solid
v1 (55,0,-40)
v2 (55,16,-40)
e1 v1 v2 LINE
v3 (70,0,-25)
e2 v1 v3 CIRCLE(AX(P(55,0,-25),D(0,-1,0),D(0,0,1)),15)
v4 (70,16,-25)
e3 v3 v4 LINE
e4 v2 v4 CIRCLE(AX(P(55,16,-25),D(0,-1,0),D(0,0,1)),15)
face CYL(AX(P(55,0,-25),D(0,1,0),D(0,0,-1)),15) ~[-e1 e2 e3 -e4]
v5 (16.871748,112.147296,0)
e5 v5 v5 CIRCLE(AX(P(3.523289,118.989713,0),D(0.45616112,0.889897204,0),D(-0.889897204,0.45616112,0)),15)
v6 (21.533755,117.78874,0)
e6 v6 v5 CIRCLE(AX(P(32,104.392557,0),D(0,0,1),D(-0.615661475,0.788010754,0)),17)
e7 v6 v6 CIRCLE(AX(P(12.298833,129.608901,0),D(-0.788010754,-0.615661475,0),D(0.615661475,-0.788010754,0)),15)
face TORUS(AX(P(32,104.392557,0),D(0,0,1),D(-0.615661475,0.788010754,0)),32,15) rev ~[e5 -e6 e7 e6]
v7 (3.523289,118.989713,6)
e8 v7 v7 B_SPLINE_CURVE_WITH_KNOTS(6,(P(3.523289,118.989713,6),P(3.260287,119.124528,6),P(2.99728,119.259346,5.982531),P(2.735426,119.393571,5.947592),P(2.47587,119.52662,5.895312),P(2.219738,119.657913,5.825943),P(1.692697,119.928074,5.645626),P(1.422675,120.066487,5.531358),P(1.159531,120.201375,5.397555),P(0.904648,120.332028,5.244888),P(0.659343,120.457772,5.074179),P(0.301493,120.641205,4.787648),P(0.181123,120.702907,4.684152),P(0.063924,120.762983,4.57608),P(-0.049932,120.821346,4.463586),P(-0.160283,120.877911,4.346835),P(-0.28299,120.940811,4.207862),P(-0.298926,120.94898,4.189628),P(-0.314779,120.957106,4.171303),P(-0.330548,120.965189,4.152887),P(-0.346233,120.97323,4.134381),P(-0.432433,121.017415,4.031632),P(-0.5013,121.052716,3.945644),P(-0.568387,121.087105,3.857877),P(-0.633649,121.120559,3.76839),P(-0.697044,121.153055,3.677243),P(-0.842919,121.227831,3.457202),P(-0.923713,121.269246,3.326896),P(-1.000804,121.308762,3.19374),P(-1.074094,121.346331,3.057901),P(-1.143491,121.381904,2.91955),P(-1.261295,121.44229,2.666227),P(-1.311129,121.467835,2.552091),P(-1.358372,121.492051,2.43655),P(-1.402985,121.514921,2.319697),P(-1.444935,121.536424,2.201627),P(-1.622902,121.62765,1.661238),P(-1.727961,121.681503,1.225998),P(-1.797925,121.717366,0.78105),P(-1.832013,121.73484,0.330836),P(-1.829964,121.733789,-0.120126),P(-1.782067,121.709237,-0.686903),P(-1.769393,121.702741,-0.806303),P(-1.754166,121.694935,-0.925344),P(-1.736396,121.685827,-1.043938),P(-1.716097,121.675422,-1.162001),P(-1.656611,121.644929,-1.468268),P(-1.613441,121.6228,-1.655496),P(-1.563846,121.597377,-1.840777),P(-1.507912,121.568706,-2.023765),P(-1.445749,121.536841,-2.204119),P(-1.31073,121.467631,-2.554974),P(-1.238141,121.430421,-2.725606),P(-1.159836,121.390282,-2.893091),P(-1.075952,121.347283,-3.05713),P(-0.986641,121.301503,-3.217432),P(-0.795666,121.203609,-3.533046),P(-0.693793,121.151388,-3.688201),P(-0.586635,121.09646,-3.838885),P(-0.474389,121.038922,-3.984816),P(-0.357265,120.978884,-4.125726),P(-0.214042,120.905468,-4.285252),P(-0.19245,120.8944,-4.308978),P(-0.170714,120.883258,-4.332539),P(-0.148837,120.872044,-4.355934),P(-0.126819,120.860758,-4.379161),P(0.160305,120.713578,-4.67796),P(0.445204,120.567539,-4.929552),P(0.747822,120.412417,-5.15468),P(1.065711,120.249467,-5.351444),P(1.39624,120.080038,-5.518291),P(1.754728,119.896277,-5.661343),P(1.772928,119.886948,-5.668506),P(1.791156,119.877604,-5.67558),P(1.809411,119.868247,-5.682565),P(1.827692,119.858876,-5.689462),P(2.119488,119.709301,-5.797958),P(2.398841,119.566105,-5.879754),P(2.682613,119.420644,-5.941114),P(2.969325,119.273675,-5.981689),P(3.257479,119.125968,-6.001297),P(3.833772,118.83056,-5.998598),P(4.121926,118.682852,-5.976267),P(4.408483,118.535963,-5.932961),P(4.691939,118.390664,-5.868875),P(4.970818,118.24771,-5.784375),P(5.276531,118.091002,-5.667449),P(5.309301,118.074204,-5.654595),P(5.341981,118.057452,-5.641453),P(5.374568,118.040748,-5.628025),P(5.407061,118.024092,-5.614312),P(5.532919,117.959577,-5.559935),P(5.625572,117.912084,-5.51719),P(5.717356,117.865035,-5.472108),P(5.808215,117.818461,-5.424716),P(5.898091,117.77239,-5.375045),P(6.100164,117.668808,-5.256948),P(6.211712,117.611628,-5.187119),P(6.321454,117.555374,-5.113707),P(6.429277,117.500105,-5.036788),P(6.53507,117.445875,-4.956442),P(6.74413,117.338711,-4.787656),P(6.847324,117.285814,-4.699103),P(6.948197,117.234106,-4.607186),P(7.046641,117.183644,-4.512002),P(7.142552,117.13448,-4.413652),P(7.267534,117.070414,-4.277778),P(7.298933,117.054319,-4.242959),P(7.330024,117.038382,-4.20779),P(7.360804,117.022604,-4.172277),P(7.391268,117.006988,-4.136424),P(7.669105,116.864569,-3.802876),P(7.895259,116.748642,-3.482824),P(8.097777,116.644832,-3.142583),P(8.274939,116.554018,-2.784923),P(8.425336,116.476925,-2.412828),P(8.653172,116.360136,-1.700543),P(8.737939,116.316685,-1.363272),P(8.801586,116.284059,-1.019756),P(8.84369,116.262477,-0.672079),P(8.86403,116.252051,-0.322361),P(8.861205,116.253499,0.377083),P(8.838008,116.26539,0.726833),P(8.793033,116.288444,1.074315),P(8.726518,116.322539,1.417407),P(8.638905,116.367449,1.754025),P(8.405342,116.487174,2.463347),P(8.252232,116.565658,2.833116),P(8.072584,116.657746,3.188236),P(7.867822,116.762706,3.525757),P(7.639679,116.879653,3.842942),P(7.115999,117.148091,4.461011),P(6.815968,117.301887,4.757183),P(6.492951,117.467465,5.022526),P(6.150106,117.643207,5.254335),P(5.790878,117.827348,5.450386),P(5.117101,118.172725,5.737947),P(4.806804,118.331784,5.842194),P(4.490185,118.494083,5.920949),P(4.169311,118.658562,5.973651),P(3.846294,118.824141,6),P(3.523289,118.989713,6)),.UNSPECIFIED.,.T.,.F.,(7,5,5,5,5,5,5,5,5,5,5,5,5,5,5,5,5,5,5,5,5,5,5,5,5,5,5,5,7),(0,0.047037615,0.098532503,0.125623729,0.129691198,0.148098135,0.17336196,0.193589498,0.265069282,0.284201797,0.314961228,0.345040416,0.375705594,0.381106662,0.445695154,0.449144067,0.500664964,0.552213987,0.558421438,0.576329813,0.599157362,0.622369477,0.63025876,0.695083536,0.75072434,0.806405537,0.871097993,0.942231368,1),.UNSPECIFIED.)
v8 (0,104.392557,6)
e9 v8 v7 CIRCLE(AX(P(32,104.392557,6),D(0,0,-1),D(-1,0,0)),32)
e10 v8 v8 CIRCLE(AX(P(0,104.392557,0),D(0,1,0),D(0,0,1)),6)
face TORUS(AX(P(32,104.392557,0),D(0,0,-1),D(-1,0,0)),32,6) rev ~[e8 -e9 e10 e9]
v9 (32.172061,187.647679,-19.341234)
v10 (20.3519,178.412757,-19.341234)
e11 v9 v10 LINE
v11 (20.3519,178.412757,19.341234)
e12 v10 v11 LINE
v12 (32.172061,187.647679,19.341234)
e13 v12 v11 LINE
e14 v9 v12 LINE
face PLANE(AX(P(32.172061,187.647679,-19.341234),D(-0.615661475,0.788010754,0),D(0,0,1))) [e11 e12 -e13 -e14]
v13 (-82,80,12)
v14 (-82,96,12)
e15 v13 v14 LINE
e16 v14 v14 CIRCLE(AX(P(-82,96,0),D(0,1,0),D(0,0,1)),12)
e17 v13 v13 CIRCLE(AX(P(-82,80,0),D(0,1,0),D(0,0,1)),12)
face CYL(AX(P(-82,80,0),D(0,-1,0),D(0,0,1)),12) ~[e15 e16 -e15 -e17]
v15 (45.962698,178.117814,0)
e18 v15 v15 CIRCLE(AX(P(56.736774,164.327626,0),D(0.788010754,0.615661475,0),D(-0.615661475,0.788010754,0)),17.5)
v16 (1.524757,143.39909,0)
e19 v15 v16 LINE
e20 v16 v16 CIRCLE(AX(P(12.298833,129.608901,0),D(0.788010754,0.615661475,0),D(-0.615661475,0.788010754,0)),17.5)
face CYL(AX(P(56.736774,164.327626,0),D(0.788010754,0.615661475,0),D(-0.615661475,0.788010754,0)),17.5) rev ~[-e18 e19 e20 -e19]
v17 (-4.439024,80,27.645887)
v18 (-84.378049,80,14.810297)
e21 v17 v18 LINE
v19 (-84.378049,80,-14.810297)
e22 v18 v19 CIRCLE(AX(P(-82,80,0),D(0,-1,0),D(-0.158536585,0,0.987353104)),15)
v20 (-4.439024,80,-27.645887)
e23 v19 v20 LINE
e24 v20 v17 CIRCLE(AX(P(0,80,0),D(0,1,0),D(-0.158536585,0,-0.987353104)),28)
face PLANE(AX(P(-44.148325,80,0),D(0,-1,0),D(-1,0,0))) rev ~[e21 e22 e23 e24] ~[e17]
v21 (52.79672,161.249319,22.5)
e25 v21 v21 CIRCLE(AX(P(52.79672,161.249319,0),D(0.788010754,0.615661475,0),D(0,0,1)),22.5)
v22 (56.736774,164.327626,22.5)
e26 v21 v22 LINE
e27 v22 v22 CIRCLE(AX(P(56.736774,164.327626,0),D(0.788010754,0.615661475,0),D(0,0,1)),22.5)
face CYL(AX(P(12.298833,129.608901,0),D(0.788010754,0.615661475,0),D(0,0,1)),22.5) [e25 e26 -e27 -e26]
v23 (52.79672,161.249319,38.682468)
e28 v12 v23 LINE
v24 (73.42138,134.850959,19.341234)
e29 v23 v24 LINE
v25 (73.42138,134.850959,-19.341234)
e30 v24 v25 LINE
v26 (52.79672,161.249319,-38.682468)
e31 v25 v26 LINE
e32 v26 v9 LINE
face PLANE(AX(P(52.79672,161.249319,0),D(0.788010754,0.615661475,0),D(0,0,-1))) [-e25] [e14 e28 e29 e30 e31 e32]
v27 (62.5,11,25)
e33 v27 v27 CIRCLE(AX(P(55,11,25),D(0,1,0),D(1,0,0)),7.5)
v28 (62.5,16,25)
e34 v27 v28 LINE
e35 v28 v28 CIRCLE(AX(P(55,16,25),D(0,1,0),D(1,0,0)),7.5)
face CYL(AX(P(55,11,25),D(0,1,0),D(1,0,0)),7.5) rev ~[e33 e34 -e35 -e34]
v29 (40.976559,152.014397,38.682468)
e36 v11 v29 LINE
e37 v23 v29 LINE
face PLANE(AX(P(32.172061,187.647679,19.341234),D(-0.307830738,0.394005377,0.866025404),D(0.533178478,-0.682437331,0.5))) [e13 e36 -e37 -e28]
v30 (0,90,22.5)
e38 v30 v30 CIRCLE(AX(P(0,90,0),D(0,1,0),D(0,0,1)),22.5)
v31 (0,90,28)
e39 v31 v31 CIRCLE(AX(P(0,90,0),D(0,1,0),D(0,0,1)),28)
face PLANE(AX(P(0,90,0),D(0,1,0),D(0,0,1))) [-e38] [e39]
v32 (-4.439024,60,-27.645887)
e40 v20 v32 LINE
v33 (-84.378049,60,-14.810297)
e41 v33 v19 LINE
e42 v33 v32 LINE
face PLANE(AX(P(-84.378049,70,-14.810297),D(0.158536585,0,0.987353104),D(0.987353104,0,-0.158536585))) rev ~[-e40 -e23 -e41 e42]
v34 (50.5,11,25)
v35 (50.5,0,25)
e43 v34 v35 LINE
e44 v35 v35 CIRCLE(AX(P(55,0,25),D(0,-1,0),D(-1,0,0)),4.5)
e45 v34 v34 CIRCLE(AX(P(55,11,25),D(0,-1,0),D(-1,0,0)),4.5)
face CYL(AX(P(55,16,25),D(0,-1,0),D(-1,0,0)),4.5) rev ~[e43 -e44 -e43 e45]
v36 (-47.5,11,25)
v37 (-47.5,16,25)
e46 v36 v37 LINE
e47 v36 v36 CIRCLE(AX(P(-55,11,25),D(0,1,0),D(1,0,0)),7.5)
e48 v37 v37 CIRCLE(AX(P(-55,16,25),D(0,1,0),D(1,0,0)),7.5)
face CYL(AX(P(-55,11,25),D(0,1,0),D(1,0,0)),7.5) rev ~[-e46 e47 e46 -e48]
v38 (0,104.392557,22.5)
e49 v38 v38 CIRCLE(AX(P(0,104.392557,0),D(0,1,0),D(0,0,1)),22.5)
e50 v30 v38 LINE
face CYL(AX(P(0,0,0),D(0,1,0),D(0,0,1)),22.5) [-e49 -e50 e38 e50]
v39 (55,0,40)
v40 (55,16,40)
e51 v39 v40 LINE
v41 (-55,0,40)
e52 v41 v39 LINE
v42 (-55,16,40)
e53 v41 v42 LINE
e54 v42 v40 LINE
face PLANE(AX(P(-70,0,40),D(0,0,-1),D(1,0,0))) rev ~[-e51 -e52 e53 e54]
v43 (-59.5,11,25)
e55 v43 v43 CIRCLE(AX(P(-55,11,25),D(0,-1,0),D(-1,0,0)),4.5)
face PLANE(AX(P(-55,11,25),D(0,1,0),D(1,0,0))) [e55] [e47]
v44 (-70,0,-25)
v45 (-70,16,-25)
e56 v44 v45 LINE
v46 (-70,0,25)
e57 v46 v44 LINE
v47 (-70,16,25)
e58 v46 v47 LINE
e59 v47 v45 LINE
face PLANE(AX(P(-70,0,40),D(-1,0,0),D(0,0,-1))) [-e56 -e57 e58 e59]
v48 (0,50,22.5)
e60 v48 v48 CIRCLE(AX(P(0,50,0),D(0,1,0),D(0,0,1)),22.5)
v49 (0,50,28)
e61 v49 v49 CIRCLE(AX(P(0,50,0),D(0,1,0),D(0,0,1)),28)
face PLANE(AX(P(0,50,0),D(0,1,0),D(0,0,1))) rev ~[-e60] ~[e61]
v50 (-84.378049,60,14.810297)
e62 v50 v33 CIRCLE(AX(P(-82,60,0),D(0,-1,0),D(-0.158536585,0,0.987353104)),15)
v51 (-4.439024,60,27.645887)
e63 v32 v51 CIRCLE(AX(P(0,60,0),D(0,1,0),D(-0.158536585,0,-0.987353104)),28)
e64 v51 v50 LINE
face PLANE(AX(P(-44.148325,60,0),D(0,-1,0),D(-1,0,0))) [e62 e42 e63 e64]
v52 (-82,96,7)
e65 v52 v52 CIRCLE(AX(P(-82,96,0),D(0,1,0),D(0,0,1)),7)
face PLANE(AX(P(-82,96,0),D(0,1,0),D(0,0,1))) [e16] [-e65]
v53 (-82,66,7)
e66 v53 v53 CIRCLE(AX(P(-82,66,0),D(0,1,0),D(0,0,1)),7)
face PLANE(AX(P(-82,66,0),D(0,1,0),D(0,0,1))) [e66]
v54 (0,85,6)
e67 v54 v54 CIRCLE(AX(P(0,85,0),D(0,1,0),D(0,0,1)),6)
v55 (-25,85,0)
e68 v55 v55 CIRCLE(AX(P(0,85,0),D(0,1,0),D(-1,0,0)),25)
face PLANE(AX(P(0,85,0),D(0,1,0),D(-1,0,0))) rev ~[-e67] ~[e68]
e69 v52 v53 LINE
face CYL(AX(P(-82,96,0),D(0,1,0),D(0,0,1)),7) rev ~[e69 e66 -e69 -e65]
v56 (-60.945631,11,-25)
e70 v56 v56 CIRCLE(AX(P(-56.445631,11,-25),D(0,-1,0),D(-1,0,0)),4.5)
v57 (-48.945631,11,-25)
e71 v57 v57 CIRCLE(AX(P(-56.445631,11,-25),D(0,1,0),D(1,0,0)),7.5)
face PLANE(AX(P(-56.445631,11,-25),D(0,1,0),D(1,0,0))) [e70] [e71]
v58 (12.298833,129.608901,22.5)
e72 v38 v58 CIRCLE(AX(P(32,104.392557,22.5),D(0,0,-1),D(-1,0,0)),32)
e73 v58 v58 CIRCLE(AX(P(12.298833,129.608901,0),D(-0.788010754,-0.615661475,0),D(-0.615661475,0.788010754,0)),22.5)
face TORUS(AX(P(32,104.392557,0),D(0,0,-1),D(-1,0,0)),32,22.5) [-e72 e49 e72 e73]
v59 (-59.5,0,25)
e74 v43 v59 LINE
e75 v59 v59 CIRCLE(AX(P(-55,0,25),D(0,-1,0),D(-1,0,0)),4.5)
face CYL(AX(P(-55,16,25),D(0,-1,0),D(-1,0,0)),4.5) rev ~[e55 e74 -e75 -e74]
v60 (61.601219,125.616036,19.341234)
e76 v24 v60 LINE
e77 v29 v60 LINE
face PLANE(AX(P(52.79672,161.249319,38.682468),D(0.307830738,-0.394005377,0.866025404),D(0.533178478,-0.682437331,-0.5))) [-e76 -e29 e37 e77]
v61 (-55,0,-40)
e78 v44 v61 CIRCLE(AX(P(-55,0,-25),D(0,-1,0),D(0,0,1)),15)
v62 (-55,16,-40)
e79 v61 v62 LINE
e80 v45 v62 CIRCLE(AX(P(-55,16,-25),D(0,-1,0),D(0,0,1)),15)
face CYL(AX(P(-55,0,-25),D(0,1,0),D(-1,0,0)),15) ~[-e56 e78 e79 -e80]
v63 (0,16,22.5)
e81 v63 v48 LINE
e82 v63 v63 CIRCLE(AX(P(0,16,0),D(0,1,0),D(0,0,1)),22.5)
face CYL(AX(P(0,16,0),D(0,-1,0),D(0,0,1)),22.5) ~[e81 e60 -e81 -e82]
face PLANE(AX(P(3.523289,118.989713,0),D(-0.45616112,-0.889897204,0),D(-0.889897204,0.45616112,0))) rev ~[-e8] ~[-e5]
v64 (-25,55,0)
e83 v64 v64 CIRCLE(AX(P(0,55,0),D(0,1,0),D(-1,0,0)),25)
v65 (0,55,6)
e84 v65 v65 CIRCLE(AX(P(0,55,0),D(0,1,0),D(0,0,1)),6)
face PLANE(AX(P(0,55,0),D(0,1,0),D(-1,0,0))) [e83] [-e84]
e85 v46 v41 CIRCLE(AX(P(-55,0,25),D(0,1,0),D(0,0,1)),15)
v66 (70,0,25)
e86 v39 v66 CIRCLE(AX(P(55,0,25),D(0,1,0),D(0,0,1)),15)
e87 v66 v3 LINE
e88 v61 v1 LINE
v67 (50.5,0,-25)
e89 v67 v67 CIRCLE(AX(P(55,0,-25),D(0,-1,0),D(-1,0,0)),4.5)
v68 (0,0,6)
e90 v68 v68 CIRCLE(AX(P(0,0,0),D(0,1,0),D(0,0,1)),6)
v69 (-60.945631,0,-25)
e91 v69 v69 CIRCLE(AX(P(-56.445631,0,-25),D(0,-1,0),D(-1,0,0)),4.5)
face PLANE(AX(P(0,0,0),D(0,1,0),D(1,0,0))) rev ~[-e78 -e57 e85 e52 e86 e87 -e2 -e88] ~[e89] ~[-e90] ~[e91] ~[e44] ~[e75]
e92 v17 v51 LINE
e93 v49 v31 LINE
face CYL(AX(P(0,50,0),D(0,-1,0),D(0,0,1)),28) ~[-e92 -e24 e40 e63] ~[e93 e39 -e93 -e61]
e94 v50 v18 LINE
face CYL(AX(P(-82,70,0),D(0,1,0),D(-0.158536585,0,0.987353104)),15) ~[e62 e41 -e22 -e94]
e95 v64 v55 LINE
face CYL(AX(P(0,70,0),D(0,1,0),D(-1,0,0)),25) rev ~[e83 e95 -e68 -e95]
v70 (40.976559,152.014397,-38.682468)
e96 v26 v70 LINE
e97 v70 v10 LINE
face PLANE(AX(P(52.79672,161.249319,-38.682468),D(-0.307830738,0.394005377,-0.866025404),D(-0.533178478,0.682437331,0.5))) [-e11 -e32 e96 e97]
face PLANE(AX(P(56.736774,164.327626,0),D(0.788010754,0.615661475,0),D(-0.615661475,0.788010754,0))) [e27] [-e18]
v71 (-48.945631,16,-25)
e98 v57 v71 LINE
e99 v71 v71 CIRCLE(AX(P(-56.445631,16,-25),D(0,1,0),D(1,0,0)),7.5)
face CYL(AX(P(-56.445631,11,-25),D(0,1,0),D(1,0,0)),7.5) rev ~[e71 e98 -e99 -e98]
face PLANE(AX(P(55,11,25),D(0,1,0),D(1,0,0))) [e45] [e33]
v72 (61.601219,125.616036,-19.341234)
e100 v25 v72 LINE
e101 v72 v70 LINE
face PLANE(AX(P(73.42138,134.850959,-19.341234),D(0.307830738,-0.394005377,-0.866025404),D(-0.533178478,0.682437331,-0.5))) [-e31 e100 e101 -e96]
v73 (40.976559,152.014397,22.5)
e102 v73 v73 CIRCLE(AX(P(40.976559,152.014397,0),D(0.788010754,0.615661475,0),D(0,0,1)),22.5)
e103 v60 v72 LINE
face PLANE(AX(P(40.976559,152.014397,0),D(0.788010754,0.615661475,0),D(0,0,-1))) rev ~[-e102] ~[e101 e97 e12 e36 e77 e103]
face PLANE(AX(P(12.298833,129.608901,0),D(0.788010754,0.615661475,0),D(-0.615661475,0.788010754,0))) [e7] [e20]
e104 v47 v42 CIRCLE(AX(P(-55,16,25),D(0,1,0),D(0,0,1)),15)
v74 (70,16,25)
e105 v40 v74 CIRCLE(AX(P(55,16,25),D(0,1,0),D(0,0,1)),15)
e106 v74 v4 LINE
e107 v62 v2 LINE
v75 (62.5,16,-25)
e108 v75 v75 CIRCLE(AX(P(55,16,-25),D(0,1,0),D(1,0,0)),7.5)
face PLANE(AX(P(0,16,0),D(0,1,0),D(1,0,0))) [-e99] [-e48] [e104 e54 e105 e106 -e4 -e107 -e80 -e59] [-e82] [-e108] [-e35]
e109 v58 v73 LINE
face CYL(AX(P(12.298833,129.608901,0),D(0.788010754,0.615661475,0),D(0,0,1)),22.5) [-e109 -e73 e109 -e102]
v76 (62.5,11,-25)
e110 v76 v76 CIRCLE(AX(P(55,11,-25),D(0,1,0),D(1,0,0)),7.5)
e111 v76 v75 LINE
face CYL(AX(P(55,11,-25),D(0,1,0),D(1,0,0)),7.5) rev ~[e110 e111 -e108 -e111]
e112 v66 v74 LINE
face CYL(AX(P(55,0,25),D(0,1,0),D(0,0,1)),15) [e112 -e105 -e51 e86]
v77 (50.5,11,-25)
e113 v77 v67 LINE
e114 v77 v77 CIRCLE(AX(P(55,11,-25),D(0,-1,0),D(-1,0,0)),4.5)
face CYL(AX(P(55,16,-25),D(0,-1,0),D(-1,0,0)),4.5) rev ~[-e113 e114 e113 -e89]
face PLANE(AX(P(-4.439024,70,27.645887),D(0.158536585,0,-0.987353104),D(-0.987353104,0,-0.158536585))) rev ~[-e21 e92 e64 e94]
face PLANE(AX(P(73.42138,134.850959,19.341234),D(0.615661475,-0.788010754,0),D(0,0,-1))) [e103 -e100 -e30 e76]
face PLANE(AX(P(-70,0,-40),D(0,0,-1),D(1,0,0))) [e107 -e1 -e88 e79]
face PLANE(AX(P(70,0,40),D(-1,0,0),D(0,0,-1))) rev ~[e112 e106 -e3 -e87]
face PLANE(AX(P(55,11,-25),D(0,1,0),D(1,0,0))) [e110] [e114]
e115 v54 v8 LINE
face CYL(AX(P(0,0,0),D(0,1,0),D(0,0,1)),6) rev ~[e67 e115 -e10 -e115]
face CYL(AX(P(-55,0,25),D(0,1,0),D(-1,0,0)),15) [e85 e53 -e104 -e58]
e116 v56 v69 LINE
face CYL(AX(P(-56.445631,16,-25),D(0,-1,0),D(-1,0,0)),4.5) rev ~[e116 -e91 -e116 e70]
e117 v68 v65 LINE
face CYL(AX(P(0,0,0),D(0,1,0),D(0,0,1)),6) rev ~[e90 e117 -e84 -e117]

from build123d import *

# Parameters (mm, degrees)
BASE_PLATE_SKETCH_W                = 140
BASE_PLATE_SKETCH_H                = 80
BASE_PLATE_140X80X16_DEPTH         = 16
LOWER_COLUMN_SKETCH_R              = 22.5
LOWER_COLUMN_45_DEPTH              = 34
UPPER_COLUMN_SKETCH_R              = 28
UPPER_COLUMN_56_DEPTH              = 40
SIDE_ARM_DEPTH                     = 10
ELBOW_SWEEP_45_PROFILE_R           = 22.5
HEX_NUT_OUTLET_DEPTH               = 15
ARM_BOSS_SKETCH_R                  = 12
ARM_BOSS_24_DEPTH                  = 16
OUTLET_BORE_SKETCH_R               = 17.5
OUTLET_BORE_35_DEPTH               = 56.392557
ELBOW_PROFILE_CUT_PROFILE_R        = 15
FLOW_PASSAGE_12_PROFILE_R          = 6
COLUMN_GROOVE_SKETCH_W             = 25
COLUMN_GROOVE_SKETCH_H             = 30
ARM_BOSS_HOLE_SKETCH_R             = 7
ARM_BOSS_HOLE_14_DEPTH             = 30
BASE_PLATE_CORNER_FILLETS_R15_R    = 15
MOUNTING_HOLES_CBORE_9_D           = 9
MOUNTING_HOLES_CBORE_9_DEPTH       = 19.773719933
MOUNTING_HOLES_CBORE_9_CBORE_D     = 15
MOUNTING_HOLES_CBORE_9_CBORE_DEPTH = 5


with BuildPart() as part:
    # Base Plate Sketch → Base Plate 140x80x16 (new body)
    with BuildSketch(Plane(origin=(0, 0, 0), x_dir=(1, 0, 0), z_dir=(0, 1, 0))):
        Rectangle(BASE_PLATE_SKETCH_W, BASE_PLATE_SKETCH_H)
    extrude(amount=BASE_PLATE_140X80X16_DEPTH)

    # Lower Column Sketch → Lower Column _45 (add)
    with BuildSketch(Plane(origin=(0, 16, 0), x_dir=(1, 0, 0), z_dir=(0, 1, 0))):
        with Locations(Location((0, 0, 0), (0, 0, 270))):
            Circle(LOWER_COLUMN_SKETCH_R)
    extrude(amount=LOWER_COLUMN_45_DEPTH)

    # Upper Column Sketch → Upper Column _56 (add)
    with BuildSketch(Plane(origin=(0, 50, 0), x_dir=(1, 0, 0), z_dir=(0, 1, 0))):
        with Locations(Location((0, 0, 0), (0, 0, 270))):
            Circle(UPPER_COLUMN_SKETCH_R)
    extrude(amount=UPPER_COLUMN_56_DEPTH)

    # Side Arm Sketch → Side Arm (add, symmetric)
    with BuildSketch(Plane(origin=(0, 70, 0), x_dir=(1, 0, 0), z_dir=(0, 1, 0))):
        with BuildLine():
            Line((-84.37804878, 14.810296553), (-4.43902439, 27.6458869))
            ThreePointArc((-4.43902439, 27.6458869), (-28, 0), (-4.43902439, -27.6458869))
            Line((-4.43902439, -27.6458869), (-84.37804878, -14.810296553))
            ThreePointArc((-84.37804878, -14.810296553), (-97, 0), (-84.37804878, 14.810296553))
        make_face()
    extrude(amount=SIDE_ARM_DEPTH, both=True)

    # Elbow Sweep _45: sweep along a path in Elbow Path Sketch
    with BuildLine(Plane.XY) as elbow_sweep_45_path:
        Line((0, 0), (0, 104.392557166))
        ThreePointArc((0, 104.392557166), (3.238590518, 118.420433863), (12.29883279, 129.608901281))
        Line((12.29883279, 129.608901281), (56.73677426, 164.327626223))
    # Elbow Sweep _45 profile (on start of the path) → Elbow Sweep _45 (sweep)
    with BuildSketch(Plane.ZX):
        Circle(ELBOW_SWEEP_45_PROFILE_R)
    sweep(path=elbow_sweep_45_path.line)

    # Hex Nut Sketch → Hex Nut Outlet (add)
    with BuildSketch(Plane(origin=(111.014464068, 86.734005111, 0), x_dir=(0, 0, -1), z_dir=(0.7880107536067209, 0.6156614753256597, 0))):
        Polygon((-38.682468036, 94.561290433), (-19.341234018, 61.061290433), (19.341234018, 61.061290433), (38.682468036, 94.561290433), (19.341234018, 128.061290433), (-19.341234018, 128.061290433), align=None)
    extrude(amount=-HEX_NUT_OUTLET_DEPTH)

    # Arm Boss Sketch → Arm Boss _24 (add)
    with BuildSketch(Plane(origin=(0, 80, 0), x_dir=(1, 0, 0), z_dir=(0, 1, 0))):
        with Locations(Location((-82, 0, 0), (0, 0, 270))):
            Circle(ARM_BOSS_SKETCH_R)
    extrude(amount=ARM_BOSS_24_DEPTH)

    # Outlet Bore Sketch → Outlet Bore _35 (cut)
    with BuildSketch(Plane(origin=(114.954517836, 89.812312487, 0), x_dir=(0, 0, -1), z_dir=(0.7880107536067209, 0.6156614753256597, 0))):
        with Locations(Location((0, 94.561290433, 0), (0, 0, 90))):
            Circle(OUTLET_BORE_SKETCH_R)
    extrude(amount=-OUTLET_BORE_35_DEPTH, mode=Mode.SUBTRACT)

    # Elbow Profile Cut: sweep along a path in Elbow Profile Cut Sketch
    with BuildLine(Plane.XY) as elbow_profile_cut_path:
        Line((56.73677426, 164.327626223), (12.29883279, 129.608901281))
        ThreePointArc((12.29883279, 129.608901281), (7.332840345, 124.777140423), (3.523289487, 118.989712997))
    # Elbow Profile Cut profile (on start of the path) → Elbow Profile Cut (sweep, cut)
    with BuildSketch(Plane(origin=(56.73677426, 164.327626223, 0), x_dir=(0.6156614753256594, -0.7880107536067211, 0), z_dir=(-0.7880107536067211, -0.6156614753256594, 0))):
        Circle(ELBOW_PROFILE_CUT_PROFILE_R)
    sweep(path=elbow_profile_cut_path.line, mode=Mode.SUBTRACT)

    # Flow Passage _12: sweep along a path in Sketch5_4
    with BuildLine(Plane.XY) as flow_passage_12_path:
        Line((0, 0), (0, 104.392557166))
        ThreePointArc((0, 104.392557166), (3.238590518, 118.420433863), (12.29883279, 129.608901281))
        Line((12.29883279, 129.608901281), (56.73677426, 164.327626223))
    # Flow Passage _12 profile (on start of the path) → Flow Passage _12 (sweep, cut)
    with BuildSketch(Plane.ZX):
        Circle(FLOW_PASSAGE_12_PROFILE_R)
    sweep(path=flow_passage_12_path.line, mode=Mode.SUBTRACT)

    # Column Groove Sketch → Column Groove (revolve, cut)
    with BuildSketch(Plane.XY):
        with Locations((-12.5, 70)):
            Rectangle(COLUMN_GROOVE_SKETCH_W, COLUMN_GROOVE_SKETCH_H)
    revolve(axis=Axis((0, 55, 0), (0, 1, 0)), mode=Mode.SUBTRACT)

    # Arm Boss Hole Sketch → Arm Boss Hole _14 (cut)
    with BuildSketch(Plane(origin=(0, 96, 0), x_dir=(1, 0, 0), z_dir=(0, 1, 0))):
        with Locations(Location((-82, 0, 0), (0, 0, 270))):
            Circle(ARM_BOSS_HOLE_SKETCH_R)
    extrude(amount=-ARM_BOSS_HOLE_14_DEPTH, mode=Mode.SUBTRACT)

    # Base Plate Corner Fillets R15
    base_plate_corner_fillets_r15_edges = [part.edges().sort_by_distance(p)[0] for p in [
        (70, 8, 40),
        (-70, 8, 40),
        (-70, 8, -40),
        (70, 8, -40),
    ]]
    fillet(base_plate_corner_fillets_r15_edges, radius=BASE_PLATE_CORNER_FILLETS_R15_R)

    # Mounting Holes CBore _9
    with Locations(Plane(origin=(0, 16, 0), x_dir=(1, 0, 0), z_dir=(0, 1, 0))):
        with Locations((55, -25), (55, 25), (-56.445631344, 25), (-55, -25)):
            CounterBoreHole(MOUNTING_HOLES_CBORE_9_D / 2, MOUNTING_HOLES_CBORE_9_CBORE_D / 2, MOUNTING_HOLES_CBORE_9_CBORE_DEPTH, depth=MOUNTING_HOLES_CBORE_9_DEPTH)


solid = part.part
